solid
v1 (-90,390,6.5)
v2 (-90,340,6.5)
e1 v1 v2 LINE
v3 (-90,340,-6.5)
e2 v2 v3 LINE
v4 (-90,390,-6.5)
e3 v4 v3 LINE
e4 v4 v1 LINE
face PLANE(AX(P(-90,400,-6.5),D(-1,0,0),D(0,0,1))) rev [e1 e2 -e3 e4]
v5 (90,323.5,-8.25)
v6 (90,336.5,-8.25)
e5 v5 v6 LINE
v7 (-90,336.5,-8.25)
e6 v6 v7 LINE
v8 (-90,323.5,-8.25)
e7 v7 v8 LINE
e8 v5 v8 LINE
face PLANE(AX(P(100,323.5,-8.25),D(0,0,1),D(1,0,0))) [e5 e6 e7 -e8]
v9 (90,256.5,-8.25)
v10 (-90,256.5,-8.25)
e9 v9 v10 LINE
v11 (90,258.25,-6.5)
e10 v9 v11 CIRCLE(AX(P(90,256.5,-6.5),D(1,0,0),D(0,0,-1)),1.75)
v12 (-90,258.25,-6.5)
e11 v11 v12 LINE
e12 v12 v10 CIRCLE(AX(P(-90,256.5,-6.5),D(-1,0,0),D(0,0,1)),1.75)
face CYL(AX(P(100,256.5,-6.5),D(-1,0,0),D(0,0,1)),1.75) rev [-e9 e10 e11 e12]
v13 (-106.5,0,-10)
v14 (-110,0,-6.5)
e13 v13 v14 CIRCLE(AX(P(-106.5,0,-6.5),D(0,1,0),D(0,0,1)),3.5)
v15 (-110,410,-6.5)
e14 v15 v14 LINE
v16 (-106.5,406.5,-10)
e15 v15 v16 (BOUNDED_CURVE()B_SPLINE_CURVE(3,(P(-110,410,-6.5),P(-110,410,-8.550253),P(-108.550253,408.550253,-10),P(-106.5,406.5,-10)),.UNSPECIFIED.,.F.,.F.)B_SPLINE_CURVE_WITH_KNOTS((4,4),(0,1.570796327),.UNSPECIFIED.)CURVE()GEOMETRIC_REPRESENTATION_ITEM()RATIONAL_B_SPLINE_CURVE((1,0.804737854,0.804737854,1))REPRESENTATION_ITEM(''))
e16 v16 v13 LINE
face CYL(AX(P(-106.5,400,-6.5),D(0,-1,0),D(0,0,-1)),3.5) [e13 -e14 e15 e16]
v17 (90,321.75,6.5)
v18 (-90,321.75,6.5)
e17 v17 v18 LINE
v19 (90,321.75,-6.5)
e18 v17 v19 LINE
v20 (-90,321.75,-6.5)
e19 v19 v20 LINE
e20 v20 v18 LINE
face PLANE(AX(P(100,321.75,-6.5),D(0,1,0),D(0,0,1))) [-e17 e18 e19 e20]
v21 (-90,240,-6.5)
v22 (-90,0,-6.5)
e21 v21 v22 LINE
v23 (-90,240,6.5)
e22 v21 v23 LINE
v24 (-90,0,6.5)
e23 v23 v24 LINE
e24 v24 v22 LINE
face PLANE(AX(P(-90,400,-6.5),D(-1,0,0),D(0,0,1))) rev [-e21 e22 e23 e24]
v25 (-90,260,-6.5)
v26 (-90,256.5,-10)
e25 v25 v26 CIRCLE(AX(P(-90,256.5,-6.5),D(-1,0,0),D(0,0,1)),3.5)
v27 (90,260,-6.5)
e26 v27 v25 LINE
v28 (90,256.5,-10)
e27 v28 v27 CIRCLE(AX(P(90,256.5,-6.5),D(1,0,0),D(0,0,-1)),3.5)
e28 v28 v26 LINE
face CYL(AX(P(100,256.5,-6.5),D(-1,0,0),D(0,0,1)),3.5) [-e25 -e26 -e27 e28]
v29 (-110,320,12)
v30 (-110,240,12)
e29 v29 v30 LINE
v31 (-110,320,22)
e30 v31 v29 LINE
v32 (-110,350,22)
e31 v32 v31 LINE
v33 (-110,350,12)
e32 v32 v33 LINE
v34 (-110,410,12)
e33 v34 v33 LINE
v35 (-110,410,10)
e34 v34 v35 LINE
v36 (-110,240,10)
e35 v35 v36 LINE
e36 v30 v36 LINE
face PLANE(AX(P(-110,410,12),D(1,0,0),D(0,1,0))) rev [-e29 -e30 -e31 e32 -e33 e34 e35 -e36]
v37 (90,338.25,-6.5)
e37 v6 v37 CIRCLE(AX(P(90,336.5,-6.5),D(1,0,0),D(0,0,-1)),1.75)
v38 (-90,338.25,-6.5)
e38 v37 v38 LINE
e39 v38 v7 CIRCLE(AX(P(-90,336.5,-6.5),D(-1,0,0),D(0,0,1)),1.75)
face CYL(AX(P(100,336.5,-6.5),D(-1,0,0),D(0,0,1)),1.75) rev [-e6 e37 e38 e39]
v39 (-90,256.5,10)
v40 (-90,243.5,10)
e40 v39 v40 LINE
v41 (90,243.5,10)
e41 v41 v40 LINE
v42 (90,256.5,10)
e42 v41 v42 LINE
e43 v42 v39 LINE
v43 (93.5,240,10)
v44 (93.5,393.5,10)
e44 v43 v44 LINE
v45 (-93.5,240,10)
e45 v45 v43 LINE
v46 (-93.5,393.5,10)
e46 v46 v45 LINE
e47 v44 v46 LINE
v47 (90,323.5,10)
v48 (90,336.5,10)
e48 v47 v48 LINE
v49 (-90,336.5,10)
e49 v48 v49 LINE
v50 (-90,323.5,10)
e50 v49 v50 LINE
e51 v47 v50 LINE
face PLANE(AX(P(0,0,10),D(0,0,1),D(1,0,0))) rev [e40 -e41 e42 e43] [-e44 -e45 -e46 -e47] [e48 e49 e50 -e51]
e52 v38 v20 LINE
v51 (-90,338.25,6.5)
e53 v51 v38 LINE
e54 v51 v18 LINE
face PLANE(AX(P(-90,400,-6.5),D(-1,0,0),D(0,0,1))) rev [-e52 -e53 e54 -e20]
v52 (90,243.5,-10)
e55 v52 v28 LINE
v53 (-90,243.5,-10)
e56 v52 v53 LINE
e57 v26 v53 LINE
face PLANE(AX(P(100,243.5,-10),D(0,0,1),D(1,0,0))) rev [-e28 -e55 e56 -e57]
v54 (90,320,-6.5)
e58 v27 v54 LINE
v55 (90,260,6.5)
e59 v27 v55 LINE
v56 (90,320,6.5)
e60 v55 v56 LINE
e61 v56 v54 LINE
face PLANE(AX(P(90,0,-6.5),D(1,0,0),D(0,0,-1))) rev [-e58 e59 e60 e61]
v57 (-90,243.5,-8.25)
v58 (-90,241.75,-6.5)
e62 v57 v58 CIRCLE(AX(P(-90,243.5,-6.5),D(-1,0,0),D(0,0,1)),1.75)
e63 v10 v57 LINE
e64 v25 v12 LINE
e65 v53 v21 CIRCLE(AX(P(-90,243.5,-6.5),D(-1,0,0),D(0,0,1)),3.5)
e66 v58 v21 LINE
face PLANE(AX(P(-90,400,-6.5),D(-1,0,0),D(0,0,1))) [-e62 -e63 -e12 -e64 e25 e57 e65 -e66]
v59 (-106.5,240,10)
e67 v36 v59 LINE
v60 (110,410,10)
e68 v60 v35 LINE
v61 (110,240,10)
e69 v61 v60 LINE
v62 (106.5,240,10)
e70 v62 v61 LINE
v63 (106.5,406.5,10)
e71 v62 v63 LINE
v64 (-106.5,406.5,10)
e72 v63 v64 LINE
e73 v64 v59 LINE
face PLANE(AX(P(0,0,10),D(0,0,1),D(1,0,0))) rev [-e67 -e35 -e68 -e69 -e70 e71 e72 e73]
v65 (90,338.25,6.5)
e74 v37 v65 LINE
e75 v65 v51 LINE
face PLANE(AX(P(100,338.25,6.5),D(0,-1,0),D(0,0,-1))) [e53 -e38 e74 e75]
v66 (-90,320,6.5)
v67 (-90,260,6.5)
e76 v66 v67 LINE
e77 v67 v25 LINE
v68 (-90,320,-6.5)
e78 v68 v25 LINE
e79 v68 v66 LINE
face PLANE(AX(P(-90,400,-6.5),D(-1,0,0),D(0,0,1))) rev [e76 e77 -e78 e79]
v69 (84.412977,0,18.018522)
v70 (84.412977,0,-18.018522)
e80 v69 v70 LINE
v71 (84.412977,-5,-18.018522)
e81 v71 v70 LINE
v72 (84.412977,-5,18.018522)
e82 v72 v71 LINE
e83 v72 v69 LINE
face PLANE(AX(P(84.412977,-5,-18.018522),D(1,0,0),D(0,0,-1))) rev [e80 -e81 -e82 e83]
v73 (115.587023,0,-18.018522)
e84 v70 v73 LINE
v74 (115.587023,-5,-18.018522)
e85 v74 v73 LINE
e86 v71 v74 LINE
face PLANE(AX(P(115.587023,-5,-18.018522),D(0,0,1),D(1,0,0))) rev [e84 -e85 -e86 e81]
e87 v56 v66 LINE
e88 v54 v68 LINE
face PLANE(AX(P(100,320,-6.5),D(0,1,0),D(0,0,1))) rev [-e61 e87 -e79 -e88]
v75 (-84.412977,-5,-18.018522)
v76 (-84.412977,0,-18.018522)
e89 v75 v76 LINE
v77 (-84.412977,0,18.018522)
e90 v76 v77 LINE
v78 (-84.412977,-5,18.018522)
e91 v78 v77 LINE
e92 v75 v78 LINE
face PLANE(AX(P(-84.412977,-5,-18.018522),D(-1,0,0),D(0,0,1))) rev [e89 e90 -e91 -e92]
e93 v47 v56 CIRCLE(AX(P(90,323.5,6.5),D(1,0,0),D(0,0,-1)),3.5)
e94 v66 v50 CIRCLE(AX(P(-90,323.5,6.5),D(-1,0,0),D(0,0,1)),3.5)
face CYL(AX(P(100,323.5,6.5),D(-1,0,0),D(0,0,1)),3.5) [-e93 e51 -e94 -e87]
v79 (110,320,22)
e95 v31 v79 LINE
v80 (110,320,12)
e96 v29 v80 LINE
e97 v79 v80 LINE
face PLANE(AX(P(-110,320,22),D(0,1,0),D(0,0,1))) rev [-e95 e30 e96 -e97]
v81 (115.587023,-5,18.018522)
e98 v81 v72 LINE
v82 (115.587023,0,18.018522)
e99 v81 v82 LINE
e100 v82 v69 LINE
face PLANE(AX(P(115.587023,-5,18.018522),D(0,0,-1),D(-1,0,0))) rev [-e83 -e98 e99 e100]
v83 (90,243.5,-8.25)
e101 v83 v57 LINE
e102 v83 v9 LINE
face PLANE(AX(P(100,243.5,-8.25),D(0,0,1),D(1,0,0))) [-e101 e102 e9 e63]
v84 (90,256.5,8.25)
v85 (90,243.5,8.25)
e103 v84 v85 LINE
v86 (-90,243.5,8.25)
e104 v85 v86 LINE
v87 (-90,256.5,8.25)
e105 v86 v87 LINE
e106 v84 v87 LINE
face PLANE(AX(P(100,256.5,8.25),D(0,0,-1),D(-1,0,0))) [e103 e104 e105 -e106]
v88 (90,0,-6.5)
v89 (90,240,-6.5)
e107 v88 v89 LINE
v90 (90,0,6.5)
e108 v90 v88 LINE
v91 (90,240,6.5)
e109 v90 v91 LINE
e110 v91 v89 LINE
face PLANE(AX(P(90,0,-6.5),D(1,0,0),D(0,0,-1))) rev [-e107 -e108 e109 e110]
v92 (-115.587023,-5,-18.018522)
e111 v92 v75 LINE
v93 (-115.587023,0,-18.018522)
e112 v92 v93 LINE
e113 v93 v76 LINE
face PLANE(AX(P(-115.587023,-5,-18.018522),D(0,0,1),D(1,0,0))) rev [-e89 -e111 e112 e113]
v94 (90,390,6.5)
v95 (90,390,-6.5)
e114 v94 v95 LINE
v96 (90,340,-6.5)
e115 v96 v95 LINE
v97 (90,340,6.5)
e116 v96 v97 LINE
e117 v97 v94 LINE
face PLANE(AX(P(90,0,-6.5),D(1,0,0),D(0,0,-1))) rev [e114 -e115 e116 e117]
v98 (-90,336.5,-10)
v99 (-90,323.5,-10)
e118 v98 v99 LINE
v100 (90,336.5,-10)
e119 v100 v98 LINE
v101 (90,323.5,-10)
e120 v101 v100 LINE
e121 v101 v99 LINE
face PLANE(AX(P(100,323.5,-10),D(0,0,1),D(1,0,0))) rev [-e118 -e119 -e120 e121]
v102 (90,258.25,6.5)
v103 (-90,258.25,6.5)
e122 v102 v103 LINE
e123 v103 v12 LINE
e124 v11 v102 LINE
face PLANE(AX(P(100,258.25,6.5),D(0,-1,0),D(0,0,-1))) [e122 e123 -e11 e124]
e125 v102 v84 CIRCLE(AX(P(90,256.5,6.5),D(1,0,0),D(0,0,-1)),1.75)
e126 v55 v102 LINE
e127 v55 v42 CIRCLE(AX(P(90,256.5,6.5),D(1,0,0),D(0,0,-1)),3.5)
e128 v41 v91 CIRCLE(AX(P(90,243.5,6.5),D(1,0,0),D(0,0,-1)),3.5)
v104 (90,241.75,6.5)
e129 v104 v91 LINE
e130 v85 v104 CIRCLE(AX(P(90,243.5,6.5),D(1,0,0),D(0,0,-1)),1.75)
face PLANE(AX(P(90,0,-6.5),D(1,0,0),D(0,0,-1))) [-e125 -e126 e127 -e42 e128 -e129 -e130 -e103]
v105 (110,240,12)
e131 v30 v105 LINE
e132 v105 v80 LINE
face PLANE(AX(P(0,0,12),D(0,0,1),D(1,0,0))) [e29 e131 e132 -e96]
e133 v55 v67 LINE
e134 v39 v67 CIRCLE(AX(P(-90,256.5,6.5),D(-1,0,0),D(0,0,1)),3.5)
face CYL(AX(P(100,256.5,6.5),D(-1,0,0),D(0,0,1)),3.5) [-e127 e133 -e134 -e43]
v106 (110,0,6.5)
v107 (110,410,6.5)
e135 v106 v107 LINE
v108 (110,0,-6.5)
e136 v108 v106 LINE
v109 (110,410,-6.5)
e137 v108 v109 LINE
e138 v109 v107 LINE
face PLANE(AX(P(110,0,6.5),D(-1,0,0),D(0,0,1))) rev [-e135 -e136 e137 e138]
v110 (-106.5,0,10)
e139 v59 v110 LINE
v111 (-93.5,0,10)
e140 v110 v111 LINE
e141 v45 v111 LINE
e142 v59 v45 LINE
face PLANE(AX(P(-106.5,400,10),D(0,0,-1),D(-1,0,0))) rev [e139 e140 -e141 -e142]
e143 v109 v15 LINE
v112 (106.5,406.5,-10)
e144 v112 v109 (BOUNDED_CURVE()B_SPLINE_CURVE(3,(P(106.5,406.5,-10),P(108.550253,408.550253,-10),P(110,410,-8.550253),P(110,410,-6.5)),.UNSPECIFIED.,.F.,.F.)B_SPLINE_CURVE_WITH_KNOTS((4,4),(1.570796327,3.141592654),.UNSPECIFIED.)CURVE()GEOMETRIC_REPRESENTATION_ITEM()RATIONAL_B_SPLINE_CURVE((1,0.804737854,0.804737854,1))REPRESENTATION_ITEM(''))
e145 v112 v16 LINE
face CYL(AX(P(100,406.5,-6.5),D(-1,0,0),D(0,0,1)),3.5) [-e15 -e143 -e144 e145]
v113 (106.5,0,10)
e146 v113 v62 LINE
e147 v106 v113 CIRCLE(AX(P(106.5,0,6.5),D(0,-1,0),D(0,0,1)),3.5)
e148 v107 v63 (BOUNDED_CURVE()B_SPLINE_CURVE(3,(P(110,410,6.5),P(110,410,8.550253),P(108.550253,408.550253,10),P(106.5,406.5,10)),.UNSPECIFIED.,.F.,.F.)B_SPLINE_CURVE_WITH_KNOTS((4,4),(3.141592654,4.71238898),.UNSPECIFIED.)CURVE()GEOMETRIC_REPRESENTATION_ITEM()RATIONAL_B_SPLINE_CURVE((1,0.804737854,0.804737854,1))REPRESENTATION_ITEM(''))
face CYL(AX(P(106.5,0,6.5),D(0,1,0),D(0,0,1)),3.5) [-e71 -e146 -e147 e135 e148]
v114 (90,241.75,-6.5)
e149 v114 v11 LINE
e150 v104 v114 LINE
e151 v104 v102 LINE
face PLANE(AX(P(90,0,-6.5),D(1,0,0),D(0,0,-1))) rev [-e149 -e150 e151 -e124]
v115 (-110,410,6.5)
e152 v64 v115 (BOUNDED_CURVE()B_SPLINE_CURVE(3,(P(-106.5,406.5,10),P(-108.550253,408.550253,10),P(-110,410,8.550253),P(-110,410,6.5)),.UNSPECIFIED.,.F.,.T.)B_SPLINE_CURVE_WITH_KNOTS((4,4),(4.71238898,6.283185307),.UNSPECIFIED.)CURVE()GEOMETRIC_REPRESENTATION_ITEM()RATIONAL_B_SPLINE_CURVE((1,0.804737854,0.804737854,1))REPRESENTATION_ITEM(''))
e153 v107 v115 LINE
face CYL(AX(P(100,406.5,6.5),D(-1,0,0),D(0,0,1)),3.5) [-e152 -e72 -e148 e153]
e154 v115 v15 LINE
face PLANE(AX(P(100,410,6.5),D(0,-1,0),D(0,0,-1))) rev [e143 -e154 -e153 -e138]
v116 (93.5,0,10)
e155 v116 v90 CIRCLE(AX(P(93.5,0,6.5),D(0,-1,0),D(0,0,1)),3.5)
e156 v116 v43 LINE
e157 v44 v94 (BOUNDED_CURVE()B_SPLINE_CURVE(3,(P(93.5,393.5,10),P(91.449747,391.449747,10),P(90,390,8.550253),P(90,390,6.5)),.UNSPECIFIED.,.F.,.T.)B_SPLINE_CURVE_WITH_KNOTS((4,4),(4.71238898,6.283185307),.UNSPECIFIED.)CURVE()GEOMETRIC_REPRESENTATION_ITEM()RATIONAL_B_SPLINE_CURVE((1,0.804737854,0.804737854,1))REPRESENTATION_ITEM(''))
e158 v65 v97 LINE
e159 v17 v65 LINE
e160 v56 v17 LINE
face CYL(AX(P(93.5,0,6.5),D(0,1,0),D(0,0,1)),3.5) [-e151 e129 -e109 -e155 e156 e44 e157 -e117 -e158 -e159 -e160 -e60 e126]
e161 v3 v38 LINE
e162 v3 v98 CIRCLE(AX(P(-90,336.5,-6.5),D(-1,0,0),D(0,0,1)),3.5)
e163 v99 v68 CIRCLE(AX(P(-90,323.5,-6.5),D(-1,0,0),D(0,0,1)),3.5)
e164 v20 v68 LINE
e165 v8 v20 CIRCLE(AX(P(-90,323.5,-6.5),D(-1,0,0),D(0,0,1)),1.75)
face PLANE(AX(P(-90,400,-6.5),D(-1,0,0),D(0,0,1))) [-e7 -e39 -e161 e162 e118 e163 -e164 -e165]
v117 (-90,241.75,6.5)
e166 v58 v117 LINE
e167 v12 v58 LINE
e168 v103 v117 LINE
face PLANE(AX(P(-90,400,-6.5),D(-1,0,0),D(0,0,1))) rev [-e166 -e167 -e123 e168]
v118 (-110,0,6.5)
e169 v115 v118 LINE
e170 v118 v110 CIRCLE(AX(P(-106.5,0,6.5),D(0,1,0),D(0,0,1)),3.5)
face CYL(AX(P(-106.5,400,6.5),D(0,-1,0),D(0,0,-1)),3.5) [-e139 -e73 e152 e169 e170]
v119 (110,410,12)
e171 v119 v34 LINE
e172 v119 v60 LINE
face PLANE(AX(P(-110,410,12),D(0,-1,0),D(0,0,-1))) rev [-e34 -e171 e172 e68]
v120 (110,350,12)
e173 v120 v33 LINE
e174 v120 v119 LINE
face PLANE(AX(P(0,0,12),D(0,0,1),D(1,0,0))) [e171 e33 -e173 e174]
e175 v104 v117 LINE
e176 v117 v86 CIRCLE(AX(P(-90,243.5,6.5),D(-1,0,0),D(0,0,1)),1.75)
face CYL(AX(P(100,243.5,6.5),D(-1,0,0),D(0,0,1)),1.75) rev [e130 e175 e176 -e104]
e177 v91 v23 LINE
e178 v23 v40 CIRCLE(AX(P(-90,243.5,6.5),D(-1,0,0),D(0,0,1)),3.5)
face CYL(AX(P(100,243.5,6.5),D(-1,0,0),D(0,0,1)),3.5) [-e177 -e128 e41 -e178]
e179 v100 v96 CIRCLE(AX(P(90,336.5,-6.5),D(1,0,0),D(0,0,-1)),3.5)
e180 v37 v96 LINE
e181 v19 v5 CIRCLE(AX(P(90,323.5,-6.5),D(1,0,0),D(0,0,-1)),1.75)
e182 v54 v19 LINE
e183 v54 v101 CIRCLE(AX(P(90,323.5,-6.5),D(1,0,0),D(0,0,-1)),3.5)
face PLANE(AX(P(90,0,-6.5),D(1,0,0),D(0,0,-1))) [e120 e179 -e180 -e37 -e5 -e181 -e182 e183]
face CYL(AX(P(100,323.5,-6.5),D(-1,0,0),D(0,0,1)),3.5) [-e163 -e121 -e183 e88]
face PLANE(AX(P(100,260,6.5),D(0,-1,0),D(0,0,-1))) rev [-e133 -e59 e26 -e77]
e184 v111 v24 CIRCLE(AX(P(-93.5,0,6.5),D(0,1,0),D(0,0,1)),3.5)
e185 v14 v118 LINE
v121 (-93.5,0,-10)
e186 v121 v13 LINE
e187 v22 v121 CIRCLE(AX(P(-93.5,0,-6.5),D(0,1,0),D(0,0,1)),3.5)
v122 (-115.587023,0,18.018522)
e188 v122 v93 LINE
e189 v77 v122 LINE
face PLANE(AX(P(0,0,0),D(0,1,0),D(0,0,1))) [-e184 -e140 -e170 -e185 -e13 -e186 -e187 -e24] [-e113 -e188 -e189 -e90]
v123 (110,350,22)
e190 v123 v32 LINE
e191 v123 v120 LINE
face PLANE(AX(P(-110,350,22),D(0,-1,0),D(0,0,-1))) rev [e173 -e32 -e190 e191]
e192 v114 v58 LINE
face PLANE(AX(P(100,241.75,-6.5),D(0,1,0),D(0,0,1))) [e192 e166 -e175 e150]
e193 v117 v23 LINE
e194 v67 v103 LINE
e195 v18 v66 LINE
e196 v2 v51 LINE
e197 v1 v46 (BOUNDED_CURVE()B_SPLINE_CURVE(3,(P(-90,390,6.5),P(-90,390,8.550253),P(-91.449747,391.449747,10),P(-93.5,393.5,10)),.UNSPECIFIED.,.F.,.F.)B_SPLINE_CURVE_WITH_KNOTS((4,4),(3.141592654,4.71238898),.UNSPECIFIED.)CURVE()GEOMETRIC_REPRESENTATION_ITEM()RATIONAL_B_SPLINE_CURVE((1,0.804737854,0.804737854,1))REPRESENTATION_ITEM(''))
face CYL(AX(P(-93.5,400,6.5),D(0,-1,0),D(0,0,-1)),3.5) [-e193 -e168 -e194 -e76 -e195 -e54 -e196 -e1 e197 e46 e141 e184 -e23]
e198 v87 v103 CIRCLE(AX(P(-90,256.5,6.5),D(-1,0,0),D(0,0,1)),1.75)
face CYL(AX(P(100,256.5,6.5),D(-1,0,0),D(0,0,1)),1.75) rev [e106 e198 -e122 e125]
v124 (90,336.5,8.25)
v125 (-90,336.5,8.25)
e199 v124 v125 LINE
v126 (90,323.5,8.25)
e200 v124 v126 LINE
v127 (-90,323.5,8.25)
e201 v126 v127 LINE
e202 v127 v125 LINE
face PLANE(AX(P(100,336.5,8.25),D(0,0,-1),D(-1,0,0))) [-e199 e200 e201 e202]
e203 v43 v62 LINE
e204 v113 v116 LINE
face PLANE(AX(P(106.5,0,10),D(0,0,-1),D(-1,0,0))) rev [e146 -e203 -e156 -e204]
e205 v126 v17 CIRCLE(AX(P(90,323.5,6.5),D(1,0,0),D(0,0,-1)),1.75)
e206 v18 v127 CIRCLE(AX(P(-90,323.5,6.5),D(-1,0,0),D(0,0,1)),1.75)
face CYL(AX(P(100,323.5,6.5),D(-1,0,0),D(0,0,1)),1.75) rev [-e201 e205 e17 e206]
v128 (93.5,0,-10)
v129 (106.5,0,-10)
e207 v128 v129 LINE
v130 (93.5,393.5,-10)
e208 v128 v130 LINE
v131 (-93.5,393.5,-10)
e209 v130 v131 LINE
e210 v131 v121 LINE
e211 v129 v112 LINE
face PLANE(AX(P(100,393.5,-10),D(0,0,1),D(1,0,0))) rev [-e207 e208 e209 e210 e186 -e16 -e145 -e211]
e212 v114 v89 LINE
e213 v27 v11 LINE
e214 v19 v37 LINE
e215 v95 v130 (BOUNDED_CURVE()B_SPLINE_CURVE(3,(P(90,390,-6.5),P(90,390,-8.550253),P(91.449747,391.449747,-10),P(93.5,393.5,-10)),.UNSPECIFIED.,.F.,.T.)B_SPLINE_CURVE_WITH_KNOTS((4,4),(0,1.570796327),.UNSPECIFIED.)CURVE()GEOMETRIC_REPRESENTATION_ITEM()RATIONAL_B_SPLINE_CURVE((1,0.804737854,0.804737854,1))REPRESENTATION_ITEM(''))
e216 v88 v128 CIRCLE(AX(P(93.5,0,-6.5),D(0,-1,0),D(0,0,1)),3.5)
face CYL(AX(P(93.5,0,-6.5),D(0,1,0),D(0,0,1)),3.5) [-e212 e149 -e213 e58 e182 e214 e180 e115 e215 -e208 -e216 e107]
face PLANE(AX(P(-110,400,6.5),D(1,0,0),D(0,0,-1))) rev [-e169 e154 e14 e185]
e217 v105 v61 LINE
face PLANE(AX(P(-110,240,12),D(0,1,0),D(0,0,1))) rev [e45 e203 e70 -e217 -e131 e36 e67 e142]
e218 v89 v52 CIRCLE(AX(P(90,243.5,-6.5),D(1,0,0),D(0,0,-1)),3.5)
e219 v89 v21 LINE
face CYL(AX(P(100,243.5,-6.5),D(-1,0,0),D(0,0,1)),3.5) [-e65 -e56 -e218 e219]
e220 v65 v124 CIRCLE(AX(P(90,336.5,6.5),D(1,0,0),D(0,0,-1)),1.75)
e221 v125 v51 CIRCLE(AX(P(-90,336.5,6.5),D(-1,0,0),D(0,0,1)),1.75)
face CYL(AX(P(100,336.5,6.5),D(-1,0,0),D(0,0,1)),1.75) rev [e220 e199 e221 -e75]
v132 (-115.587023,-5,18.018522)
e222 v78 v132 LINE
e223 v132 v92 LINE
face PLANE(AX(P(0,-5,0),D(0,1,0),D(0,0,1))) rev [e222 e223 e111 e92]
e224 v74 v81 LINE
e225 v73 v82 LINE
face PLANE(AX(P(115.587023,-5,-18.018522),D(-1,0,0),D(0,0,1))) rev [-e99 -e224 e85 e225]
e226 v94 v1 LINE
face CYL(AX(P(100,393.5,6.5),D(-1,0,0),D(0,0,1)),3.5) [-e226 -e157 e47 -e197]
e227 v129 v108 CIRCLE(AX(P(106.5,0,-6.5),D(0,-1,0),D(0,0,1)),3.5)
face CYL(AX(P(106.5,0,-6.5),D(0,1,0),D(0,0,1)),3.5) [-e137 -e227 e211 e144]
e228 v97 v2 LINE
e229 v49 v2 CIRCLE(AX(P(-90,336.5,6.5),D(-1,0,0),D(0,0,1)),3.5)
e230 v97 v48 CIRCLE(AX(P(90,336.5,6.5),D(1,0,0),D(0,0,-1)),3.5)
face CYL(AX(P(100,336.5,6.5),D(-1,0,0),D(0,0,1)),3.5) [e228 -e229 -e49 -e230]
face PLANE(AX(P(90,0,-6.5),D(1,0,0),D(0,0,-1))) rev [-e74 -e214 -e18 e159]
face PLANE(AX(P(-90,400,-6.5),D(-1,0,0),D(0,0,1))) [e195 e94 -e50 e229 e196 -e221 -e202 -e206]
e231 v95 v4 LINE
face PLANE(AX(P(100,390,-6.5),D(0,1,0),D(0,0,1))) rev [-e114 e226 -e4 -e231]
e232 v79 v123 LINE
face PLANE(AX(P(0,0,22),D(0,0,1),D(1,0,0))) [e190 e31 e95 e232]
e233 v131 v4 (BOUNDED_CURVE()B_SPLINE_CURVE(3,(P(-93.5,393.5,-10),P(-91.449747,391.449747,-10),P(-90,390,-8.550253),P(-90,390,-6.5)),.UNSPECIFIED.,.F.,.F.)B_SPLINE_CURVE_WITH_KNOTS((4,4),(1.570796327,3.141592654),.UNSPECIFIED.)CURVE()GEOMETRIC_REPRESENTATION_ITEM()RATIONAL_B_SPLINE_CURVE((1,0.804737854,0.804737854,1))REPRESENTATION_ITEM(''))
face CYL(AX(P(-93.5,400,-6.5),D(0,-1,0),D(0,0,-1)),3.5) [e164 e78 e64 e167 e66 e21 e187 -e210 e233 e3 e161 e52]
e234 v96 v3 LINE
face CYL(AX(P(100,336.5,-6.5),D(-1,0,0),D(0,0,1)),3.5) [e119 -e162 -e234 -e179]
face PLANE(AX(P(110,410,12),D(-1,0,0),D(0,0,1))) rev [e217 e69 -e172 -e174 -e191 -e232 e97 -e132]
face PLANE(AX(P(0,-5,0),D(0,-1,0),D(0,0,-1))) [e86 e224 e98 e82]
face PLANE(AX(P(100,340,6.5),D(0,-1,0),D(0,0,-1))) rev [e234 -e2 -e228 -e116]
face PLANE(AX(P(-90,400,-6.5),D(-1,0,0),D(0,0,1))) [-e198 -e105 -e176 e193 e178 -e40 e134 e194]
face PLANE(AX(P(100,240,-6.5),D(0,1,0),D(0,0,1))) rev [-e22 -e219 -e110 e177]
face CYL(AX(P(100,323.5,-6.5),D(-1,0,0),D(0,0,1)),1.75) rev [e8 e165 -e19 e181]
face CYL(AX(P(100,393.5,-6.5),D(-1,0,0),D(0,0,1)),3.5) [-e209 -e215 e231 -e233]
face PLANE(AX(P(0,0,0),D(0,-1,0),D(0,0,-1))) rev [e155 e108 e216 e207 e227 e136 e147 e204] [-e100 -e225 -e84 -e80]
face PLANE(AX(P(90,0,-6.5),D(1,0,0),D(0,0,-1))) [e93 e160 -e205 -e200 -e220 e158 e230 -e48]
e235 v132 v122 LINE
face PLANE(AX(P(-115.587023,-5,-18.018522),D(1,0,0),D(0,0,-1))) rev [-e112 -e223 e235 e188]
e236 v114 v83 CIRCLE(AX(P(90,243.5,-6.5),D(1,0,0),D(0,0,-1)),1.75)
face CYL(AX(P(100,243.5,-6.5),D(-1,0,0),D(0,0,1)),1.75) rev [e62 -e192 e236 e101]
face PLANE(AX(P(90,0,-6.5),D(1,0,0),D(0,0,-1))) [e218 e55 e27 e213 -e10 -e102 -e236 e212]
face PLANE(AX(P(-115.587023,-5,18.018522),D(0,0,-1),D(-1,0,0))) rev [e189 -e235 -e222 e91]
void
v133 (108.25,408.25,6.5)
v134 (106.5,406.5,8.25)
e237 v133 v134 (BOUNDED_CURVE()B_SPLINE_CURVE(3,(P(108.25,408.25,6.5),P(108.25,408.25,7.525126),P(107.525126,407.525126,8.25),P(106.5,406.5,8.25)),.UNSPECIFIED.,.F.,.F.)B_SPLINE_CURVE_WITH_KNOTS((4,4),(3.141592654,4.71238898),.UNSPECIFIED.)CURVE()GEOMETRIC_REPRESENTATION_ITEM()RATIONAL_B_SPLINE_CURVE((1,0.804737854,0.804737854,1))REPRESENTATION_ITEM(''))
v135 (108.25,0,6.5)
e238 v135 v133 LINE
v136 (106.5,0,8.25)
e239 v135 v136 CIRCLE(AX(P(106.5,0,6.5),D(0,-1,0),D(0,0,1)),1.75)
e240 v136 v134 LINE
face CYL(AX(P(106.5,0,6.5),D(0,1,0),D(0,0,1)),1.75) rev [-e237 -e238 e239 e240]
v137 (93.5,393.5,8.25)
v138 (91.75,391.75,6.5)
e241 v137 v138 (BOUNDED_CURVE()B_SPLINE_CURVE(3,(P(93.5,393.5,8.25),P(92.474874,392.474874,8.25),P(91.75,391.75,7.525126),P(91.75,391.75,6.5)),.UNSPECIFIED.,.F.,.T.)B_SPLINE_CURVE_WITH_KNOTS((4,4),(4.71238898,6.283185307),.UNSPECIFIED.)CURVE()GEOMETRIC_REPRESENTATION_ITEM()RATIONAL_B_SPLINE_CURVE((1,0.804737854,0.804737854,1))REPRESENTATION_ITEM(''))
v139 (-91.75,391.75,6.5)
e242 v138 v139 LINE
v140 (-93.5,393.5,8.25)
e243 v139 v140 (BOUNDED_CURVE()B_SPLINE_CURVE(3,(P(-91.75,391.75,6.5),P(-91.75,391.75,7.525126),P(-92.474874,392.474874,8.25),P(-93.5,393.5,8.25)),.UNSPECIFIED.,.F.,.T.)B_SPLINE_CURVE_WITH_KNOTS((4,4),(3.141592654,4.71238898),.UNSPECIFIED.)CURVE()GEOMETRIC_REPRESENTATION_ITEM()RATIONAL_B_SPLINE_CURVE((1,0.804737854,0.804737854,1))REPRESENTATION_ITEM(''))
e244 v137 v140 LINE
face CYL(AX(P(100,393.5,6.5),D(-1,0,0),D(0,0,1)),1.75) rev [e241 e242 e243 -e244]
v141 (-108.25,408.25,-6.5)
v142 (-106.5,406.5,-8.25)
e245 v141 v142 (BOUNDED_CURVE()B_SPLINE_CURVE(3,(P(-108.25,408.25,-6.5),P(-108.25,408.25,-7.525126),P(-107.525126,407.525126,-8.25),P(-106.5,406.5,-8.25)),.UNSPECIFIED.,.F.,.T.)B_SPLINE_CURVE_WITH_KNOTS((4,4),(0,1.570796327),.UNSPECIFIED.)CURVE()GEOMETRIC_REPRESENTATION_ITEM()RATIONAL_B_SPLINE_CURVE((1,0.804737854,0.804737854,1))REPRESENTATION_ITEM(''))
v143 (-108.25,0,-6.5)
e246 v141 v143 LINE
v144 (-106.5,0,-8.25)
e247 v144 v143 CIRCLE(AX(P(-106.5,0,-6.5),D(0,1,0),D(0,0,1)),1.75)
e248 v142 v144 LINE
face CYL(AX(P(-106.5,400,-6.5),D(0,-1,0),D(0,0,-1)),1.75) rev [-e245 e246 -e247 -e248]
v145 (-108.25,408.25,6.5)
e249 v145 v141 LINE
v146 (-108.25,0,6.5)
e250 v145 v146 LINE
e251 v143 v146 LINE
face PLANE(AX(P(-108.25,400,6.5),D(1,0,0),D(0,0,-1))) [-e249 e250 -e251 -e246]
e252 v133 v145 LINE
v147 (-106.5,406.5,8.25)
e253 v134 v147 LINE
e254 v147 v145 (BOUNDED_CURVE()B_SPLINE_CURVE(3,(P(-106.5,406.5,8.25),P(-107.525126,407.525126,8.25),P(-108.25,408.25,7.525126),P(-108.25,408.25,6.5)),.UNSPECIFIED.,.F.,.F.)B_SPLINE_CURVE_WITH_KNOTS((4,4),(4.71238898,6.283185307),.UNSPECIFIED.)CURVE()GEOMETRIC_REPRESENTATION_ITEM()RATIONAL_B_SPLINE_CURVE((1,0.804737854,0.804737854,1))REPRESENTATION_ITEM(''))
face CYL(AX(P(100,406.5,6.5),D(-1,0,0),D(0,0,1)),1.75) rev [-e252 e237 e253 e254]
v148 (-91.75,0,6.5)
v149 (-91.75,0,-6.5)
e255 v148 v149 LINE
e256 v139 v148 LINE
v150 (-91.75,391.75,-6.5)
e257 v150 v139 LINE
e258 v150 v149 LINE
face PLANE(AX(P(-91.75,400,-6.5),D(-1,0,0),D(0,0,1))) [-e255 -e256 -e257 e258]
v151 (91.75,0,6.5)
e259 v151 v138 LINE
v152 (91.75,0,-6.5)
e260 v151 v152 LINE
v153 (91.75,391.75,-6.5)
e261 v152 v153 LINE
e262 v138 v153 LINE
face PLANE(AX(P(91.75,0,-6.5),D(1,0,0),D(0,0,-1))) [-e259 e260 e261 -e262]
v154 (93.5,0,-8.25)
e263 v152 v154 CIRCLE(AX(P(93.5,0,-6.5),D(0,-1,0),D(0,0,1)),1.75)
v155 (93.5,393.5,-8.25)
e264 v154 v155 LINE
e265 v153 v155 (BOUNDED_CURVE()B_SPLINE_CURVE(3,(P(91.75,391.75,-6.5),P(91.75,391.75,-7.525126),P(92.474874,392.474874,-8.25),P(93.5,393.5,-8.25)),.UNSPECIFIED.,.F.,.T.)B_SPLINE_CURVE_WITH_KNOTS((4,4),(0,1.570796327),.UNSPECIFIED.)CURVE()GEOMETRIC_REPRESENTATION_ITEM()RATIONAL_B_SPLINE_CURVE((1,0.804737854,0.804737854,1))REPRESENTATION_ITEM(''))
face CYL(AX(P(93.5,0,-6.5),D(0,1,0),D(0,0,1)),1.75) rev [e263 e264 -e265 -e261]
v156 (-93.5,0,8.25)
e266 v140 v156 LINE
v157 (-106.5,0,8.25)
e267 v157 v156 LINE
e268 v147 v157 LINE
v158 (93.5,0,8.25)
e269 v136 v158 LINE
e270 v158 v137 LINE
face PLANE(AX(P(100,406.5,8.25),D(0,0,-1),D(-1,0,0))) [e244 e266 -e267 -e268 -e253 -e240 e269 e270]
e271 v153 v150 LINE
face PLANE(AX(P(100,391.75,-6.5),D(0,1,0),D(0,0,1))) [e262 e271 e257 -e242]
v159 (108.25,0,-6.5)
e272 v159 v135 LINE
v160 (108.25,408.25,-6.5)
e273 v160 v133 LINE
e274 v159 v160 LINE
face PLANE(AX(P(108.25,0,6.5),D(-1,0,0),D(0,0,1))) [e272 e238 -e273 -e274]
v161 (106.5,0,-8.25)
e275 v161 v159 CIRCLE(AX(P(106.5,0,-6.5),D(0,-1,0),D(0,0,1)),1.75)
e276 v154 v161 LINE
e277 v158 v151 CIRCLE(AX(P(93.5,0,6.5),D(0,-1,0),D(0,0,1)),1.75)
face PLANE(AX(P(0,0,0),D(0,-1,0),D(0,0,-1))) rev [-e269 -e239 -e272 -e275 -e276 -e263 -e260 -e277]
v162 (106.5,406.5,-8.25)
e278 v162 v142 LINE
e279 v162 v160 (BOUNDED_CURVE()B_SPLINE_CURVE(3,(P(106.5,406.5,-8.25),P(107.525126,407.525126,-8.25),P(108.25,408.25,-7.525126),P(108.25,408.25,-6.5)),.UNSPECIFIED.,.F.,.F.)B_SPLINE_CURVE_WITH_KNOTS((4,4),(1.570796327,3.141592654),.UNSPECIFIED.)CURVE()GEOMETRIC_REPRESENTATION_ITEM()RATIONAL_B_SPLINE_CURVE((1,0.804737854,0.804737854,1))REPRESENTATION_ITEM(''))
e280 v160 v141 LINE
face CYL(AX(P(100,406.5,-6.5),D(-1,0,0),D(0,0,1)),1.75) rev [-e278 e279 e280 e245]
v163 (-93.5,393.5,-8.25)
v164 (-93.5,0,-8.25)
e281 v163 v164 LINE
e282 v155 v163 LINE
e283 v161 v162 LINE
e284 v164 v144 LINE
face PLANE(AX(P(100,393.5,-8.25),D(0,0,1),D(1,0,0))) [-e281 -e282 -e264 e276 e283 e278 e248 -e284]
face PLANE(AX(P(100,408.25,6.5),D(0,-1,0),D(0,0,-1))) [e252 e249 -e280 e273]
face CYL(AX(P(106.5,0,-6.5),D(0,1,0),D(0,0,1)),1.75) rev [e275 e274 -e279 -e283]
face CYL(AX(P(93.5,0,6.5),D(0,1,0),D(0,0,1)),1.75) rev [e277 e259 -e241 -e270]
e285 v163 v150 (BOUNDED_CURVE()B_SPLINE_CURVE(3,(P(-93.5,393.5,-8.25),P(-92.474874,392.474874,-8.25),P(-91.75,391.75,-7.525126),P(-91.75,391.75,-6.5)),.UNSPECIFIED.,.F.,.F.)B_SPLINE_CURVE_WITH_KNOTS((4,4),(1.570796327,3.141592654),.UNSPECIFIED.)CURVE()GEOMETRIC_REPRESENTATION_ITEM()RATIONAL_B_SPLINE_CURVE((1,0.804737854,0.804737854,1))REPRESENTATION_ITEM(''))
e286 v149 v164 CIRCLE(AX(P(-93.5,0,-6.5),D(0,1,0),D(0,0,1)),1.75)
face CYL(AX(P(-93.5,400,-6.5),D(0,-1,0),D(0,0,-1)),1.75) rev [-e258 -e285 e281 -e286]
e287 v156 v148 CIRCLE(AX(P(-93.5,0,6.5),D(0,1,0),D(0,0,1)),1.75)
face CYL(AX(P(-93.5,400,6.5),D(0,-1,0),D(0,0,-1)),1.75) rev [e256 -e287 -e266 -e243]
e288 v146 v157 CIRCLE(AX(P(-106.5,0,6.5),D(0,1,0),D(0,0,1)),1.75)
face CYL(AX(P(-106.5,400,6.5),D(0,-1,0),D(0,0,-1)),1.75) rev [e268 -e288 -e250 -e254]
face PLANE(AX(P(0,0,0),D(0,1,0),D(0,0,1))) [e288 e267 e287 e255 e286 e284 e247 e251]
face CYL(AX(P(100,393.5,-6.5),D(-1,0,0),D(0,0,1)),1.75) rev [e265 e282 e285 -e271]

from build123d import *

# Parameters (mm, degrees)
GB_6728_1986_SQUARE_HOLLOW_SECTION_020_X_DEPTH = 415.142135624
GB_6728_1986_SQUARE_HOLLOW_SECTION_0_3_DEPTH   = 230.284271247
GB_6728_1986_SQUARE_HOLLOW_SECTION_0_5_DEPTH   = 415.142135624
GB_6728_1986_SQUARE_HOLLOW_SECTION_0_6_DEPTH   = 202
GB_6728_1986_SQUARE_HOLLOW_SECTION_0_8_DEPTH   = 202
SKETCH2_W                                      = 31.17404588
SKETCH2_H                                      = 36.03704403
BOSS_EXTRUDE1_DEPTH                            = 5
SKETCH3_W                                      = 220
SKETCH3_H                                      = 170
BOSS_EXTRUDE2_DEPTH                            = 2
SKETCH4_W                                      = 220
SKETCH4_H                                      = 30
BOSS_EXTRUDE3_DEPTH                            = 10


with BuildPart() as part:
    # Sketch1 → GB/6728-1986 square hollow section 020 X 20 X 1.75(1) (new body)
    with BuildSketch(Plane(origin=(-100, 0, 0), x_dir=(-1, 0, 0), z_dir=(0, 1, 0))):
        with BuildLine():
            Line((-6.5, -10), (6.5, -10))
            ThreePointArc((6.5, -10), (8.974873734, -8.974873734), (10, -6.5))
            Line((10, -6.5), (10, 6.5))
            ThreePointArc((10, 6.5), (8.974873734, 8.974873734), (6.5, 10))
            Line((6.5, 10), (-6.5, 10))
            ThreePointArc((-6.5, 10), (-8.974873734, 8.974873734), (-10, 6.5))
            Line((-10, 6.5), (-10, -6.5))
            ThreePointArc((-10, -6.5), (-8.974873734, -8.974873734), (-6.5, -10))
        make_face()
        with BuildLine():
            Line((-6.5, -8.25), (6.5, -8.25))
            ThreePointArc((6.5, -8.25), (7.737436867, -7.737436867), (8.25, -6.5))
            Line((8.25, -6.5), (8.25, 6.5))
            ThreePointArc((8.25, 6.5), (7.737436867, 7.737436867), (6.5, 8.25))
            Line((6.5, 8.25), (-6.5, 8.25))
            ThreePointArc((-6.5, 8.25), (-7.737436867, 7.737436867), (-8.25, 6.5))
            Line((-8.25, 6.5), (-8.25, -6.5))
            ThreePointArc((-8.25, -6.5), (-7.737436867, -7.737436867), (-6.5, -8.25))
        make_face(mode=Mode.SUBTRACT)
    extrude(amount=GB_6728_1986_SQUARE_HOLLOW_SECTION_020_X_DEPTH)

    # GB_6728-1986 square hollow section 0 2
    split(bisect_by=Plane(origin=(-100, 400, 0), x_dir=(0.707106781, -0.707106781, 0), z_dir=(-0.707106781, -0.707106781, 0)), keep=Keep.TOP)



with BuildPart() as body_2:
    # Sketch1 on segment 2 (carried to segment 2) → GB_6728-1986 square hollow section 0 3 (new body)
    with BuildSketch(Plane(origin=(-115.142135624, 400, 0), x_dir=(0, 1, 0), z_dir=(1, 0, 0))):
        with BuildLine():
            Line((-6.5, -10), (6.5, -10))
            ThreePointArc((6.5, -10), (8.974873734, -8.974873734), (10, -6.5))
            Line((10, -6.5), (10, 6.5))
            ThreePointArc((10, 6.5), (8.974873734, 8.974873734), (6.5, 10))
            Line((6.5, 10), (-6.5, 10))
            ThreePointArc((-6.5, 10), (-8.974873734, 8.974873734), (-10, 6.5))
            Line((-10, 6.5), (-10, -6.5))
            ThreePointArc((-10, -6.5), (-8.974873734, -8.974873734), (-6.5, -10))
        make_face()
        with BuildLine():
            Line((-6.5, -8.25), (6.5, -8.25))
            ThreePointArc((6.5, -8.25), (7.737436867, -7.737436867), (8.25, -6.5))
            Line((8.25, -6.5), (8.25, 6.5))
            ThreePointArc((8.25, 6.5), (7.737436867, 7.737436867), (6.5, 8.25))
            Line((6.5, 8.25), (-6.5, 8.25))
            ThreePointArc((-6.5, 8.25), (-7.737436867, 7.737436867), (-8.25, 6.5))
            Line((-8.25, 6.5), (-8.25, -6.5))
            ThreePointArc((-8.25, -6.5), (-7.737436867, -7.737436867), (-6.5, -8.25))
        make_face(mode=Mode.SUBTRACT)
    extrude(amount=GB_6728_1986_SQUARE_HOLLOW_SECTION_0_3_DEPTH)

    # GB_6728-1986 square hollow section 0 3 m
    split(bisect_by=Plane(origin=(-100, 400, 0), x_dir=(-0.707106781, 0.707106781, 0), z_dir=(0.707106781, 0.707106781, 0)), keep=Keep.TOP)

    # GB_6728-1986 square hollow section 0 4
    split(bisect_by=Plane(origin=(100, 400, 0), x_dir=(-0.707106781, -0.707106781, 0), z_dir=(-0.707106781, 0.707106781, 0)), keep=Keep.TOP)


with BuildPart() as body_3:
    # Sketch1 on segment 3 (carried to segment 3) → GB_6728-1986 square hollow section 0 5 (new body)
    with BuildSketch(Plane(origin=(100, 415.142135624, 0), x_dir=(1, 0, 0), z_dir=(0, -1, 0))):
        with BuildLine():
            Line((-6.5, -10), (6.5, -10))
            ThreePointArc((6.5, -10), (8.974873734, -8.974873734), (10, -6.5))
            Line((10, -6.5), (10, 6.5))
            ThreePointArc((10, 6.5), (8.974873734, 8.974873734), (6.5, 10))
            Line((6.5, 10), (-6.5, 10))
            ThreePointArc((-6.5, 10), (-8.974873734, 8.974873734), (-10, 6.5))
            Line((-10, 6.5), (-10, -6.5))
            ThreePointArc((-10, -6.5), (-8.974873734, -8.974873734), (-6.5, -10))
        make_face()
        with BuildLine():
            Line((-6.5, -8.25), (6.5, -8.25))
            ThreePointArc((6.5, -8.25), (7.737436867, -7.737436867), (8.25, -6.5))
            Line((8.25, -6.5), (8.25, 6.5))
            ThreePointArc((8.25, 6.5), (7.737436867, 7.737436867), (6.5, 8.25))
            Line((6.5, 8.25), (-6.5, 8.25))
            ThreePointArc((-6.5, 8.25), (-7.737436867, 7.737436867), (-8.25, 6.5))
            Line((-8.25, 6.5), (-8.25, -6.5))
            ThreePointArc((-8.25, -6.5), (-7.737436867, -7.737436867), (-6.5, -8.25))
        make_face(mode=Mode.SUBTRACT)
    extrude(amount=GB_6728_1986_SQUARE_HOLLOW_SECTION_0_5_DEPTH)

    # GB_6728-1986 square hollow section 0 5 m
    split(bisect_by=Plane(origin=(100, 400, 0), x_dir=(0.707106781, 0.707106781, 0), z_dir=(0.707106781, -0.707106781, 0)), keep=Keep.TOP)


with BuildPart() as body_4:
    # Sketch1 on segment 4 (carried to segment 4) → GB_6728-1986 square hollow section 0 6 (new body)
    with BuildSketch(Plane(origin=(-101, 330, 0), x_dir=(0, 1, 0), z_dir=(1, 0, 0))):
        with BuildLine():
            Line((-6.5, -10), (6.5, -10))
            ThreePointArc((6.5, -10), (8.974873734, -8.974873734), (10, -6.5))
            Line((10, -6.5), (10, 6.5))
            ThreePointArc((10, 6.5), (8.974873734, 8.974873734), (6.5, 10))
            Line((6.5, 10), (-6.5, 10))
            ThreePointArc((-6.5, 10), (-8.974873734, 8.974873734), (-10, 6.5))
            Line((-10, 6.5), (-10, -6.5))
            ThreePointArc((-10, -6.5), (-8.974873734, -8.974873734), (-6.5, -10))
        make_face()
        with BuildLine():
            Line((-6.5, -8.25), (6.5, -8.25))
            ThreePointArc((6.5, -8.25), (7.737436867, -7.737436867), (8.25, -6.5))
            Line((8.25, -6.5), (8.25, 6.5))
            ThreePointArc((8.25, 6.5), (7.737436867, 7.737436867), (6.5, 8.25))
            Line((6.5, 8.25), (-6.5, 8.25))
            ThreePointArc((-6.5, 8.25), (-7.737436867, 7.737436867), (-8.25, 6.5))
            Line((-8.25, 6.5), (-8.25, -6.5))
            ThreePointArc((-8.25, -6.5), (-7.737436867, -7.737436867), (-6.5, -8.25))
        make_face(mode=Mode.SUBTRACT)
    extrude(amount=GB_6728_1986_SQUARE_HOLLOW_SECTION_0_6_DEPTH)

    # GB_6728-1986 square hollow section 0 6 m
    split(bisect_by=Plane(origin=(-90, 330, 0), x_dir=(0, 1, 0), z_dir=(1, 0, 0)), keep=Keep.TOP)

    # GB_6728-1986 square hollow section 0 7
    split(bisect_by=Plane(origin=(90, 330, 0), x_dir=(0, -1, 0), z_dir=(-1, 0, 0)), keep=Keep.TOP)


with BuildPart() as body_5:
    # Sketch1 on segment 5 (carried to segment 5) → GB_6728-1986 square hollow section 0 8 (new body)
    with BuildSketch(Plane(origin=(-101, 250, 0), x_dir=(0, 1, 0), z_dir=(1, 0, 0))):
        with BuildLine():
            Line((-6.5, -10), (6.5, -10))
            ThreePointArc((6.5, -10), (8.974873734, -8.974873734), (10, -6.5))
            Line((10, -6.5), (10, 6.5))
            ThreePointArc((10, 6.5), (8.974873734, 8.974873734), (6.5, 10))
            Line((6.5, 10), (-6.5, 10))
            ThreePointArc((-6.5, 10), (-8.974873734, 8.974873734), (-10, 6.5))
            Line((-10, 6.5), (-10, -6.5))
            ThreePointArc((-10, -6.5), (-8.974873734, -8.974873734), (-6.5, -10))
        make_face()
        with BuildLine():
            Line((-6.5, -8.25), (6.5, -8.25))
            ThreePointArc((6.5, -8.25), (7.737436867, -7.737436867), (8.25, -6.5))
            Line((8.25, -6.5), (8.25, 6.5))
            ThreePointArc((8.25, 6.5), (7.737436867, 7.737436867), (6.5, 8.25))
            Line((6.5, 8.25), (-6.5, 8.25))
            ThreePointArc((-6.5, 8.25), (-7.737436867, 7.737436867), (-8.25, 6.5))
            Line((-8.25, 6.5), (-8.25, -6.5))
            ThreePointArc((-8.25, -6.5), (-7.737436867, -7.737436867), (-6.5, -8.25))
        make_face(mode=Mode.SUBTRACT)
    extrude(amount=GB_6728_1986_SQUARE_HOLLOW_SECTION_0_8_DEPTH)

    # GB_6728-1986 square hollow section 0 8 m
    split(bisect_by=Plane(origin=(-90, 250, 0), x_dir=(0, 1, 0), z_dir=(1, 0, 0)), keep=Keep.TOP)

    # GB_6728-1986 square hollow section 0 9
    split(bisect_by=Plane(origin=(90, 250, 0), x_dir=(0, -1, 0), z_dir=(-1, 0, 0)), keep=Keep.TOP)


with BuildPart() as part_1:
    add(part.part)

    add(body_3.part)  # Boss-Extrude1 merges body 3
    # Sketch2 → Boss-Extrude1 (add)
    with BuildSketch(Plane.XZ):
        with Locations((-100, 0)):
            Rectangle(SKETCH2_W, SKETCH2_H)
        with Locations((100, 0)):
            Rectangle(SKETCH2_W, SKETCH2_H)
    extrude(amount=BOSS_EXTRUDE1_DEPTH)


    add(body_2.part)  # Boss-Extrude2 merges body 2

    add(body_4.part)  # Boss-Extrude2 merges body 4

    add(body_5.part)  # Boss-Extrude2 merges body 5
    # Sketch3 → Boss-Extrude2 (add)
    with BuildSketch(Plane.XY.offset(10)):
        with Locations((0, 325)):
            Rectangle(SKETCH3_W, SKETCH3_H)
    extrude(amount=BOSS_EXTRUDE2_DEPTH)

    # Sketch4 → Boss-Extrude3 (add)
    with BuildSketch(Plane.XY.offset(12)):
        with Locations((0, 335)):
            Rectangle(SKETCH4_W, SKETCH4_H)
    extrude(amount=BOSS_EXTRUDE3_DEPTH)


solid = part_1.part
